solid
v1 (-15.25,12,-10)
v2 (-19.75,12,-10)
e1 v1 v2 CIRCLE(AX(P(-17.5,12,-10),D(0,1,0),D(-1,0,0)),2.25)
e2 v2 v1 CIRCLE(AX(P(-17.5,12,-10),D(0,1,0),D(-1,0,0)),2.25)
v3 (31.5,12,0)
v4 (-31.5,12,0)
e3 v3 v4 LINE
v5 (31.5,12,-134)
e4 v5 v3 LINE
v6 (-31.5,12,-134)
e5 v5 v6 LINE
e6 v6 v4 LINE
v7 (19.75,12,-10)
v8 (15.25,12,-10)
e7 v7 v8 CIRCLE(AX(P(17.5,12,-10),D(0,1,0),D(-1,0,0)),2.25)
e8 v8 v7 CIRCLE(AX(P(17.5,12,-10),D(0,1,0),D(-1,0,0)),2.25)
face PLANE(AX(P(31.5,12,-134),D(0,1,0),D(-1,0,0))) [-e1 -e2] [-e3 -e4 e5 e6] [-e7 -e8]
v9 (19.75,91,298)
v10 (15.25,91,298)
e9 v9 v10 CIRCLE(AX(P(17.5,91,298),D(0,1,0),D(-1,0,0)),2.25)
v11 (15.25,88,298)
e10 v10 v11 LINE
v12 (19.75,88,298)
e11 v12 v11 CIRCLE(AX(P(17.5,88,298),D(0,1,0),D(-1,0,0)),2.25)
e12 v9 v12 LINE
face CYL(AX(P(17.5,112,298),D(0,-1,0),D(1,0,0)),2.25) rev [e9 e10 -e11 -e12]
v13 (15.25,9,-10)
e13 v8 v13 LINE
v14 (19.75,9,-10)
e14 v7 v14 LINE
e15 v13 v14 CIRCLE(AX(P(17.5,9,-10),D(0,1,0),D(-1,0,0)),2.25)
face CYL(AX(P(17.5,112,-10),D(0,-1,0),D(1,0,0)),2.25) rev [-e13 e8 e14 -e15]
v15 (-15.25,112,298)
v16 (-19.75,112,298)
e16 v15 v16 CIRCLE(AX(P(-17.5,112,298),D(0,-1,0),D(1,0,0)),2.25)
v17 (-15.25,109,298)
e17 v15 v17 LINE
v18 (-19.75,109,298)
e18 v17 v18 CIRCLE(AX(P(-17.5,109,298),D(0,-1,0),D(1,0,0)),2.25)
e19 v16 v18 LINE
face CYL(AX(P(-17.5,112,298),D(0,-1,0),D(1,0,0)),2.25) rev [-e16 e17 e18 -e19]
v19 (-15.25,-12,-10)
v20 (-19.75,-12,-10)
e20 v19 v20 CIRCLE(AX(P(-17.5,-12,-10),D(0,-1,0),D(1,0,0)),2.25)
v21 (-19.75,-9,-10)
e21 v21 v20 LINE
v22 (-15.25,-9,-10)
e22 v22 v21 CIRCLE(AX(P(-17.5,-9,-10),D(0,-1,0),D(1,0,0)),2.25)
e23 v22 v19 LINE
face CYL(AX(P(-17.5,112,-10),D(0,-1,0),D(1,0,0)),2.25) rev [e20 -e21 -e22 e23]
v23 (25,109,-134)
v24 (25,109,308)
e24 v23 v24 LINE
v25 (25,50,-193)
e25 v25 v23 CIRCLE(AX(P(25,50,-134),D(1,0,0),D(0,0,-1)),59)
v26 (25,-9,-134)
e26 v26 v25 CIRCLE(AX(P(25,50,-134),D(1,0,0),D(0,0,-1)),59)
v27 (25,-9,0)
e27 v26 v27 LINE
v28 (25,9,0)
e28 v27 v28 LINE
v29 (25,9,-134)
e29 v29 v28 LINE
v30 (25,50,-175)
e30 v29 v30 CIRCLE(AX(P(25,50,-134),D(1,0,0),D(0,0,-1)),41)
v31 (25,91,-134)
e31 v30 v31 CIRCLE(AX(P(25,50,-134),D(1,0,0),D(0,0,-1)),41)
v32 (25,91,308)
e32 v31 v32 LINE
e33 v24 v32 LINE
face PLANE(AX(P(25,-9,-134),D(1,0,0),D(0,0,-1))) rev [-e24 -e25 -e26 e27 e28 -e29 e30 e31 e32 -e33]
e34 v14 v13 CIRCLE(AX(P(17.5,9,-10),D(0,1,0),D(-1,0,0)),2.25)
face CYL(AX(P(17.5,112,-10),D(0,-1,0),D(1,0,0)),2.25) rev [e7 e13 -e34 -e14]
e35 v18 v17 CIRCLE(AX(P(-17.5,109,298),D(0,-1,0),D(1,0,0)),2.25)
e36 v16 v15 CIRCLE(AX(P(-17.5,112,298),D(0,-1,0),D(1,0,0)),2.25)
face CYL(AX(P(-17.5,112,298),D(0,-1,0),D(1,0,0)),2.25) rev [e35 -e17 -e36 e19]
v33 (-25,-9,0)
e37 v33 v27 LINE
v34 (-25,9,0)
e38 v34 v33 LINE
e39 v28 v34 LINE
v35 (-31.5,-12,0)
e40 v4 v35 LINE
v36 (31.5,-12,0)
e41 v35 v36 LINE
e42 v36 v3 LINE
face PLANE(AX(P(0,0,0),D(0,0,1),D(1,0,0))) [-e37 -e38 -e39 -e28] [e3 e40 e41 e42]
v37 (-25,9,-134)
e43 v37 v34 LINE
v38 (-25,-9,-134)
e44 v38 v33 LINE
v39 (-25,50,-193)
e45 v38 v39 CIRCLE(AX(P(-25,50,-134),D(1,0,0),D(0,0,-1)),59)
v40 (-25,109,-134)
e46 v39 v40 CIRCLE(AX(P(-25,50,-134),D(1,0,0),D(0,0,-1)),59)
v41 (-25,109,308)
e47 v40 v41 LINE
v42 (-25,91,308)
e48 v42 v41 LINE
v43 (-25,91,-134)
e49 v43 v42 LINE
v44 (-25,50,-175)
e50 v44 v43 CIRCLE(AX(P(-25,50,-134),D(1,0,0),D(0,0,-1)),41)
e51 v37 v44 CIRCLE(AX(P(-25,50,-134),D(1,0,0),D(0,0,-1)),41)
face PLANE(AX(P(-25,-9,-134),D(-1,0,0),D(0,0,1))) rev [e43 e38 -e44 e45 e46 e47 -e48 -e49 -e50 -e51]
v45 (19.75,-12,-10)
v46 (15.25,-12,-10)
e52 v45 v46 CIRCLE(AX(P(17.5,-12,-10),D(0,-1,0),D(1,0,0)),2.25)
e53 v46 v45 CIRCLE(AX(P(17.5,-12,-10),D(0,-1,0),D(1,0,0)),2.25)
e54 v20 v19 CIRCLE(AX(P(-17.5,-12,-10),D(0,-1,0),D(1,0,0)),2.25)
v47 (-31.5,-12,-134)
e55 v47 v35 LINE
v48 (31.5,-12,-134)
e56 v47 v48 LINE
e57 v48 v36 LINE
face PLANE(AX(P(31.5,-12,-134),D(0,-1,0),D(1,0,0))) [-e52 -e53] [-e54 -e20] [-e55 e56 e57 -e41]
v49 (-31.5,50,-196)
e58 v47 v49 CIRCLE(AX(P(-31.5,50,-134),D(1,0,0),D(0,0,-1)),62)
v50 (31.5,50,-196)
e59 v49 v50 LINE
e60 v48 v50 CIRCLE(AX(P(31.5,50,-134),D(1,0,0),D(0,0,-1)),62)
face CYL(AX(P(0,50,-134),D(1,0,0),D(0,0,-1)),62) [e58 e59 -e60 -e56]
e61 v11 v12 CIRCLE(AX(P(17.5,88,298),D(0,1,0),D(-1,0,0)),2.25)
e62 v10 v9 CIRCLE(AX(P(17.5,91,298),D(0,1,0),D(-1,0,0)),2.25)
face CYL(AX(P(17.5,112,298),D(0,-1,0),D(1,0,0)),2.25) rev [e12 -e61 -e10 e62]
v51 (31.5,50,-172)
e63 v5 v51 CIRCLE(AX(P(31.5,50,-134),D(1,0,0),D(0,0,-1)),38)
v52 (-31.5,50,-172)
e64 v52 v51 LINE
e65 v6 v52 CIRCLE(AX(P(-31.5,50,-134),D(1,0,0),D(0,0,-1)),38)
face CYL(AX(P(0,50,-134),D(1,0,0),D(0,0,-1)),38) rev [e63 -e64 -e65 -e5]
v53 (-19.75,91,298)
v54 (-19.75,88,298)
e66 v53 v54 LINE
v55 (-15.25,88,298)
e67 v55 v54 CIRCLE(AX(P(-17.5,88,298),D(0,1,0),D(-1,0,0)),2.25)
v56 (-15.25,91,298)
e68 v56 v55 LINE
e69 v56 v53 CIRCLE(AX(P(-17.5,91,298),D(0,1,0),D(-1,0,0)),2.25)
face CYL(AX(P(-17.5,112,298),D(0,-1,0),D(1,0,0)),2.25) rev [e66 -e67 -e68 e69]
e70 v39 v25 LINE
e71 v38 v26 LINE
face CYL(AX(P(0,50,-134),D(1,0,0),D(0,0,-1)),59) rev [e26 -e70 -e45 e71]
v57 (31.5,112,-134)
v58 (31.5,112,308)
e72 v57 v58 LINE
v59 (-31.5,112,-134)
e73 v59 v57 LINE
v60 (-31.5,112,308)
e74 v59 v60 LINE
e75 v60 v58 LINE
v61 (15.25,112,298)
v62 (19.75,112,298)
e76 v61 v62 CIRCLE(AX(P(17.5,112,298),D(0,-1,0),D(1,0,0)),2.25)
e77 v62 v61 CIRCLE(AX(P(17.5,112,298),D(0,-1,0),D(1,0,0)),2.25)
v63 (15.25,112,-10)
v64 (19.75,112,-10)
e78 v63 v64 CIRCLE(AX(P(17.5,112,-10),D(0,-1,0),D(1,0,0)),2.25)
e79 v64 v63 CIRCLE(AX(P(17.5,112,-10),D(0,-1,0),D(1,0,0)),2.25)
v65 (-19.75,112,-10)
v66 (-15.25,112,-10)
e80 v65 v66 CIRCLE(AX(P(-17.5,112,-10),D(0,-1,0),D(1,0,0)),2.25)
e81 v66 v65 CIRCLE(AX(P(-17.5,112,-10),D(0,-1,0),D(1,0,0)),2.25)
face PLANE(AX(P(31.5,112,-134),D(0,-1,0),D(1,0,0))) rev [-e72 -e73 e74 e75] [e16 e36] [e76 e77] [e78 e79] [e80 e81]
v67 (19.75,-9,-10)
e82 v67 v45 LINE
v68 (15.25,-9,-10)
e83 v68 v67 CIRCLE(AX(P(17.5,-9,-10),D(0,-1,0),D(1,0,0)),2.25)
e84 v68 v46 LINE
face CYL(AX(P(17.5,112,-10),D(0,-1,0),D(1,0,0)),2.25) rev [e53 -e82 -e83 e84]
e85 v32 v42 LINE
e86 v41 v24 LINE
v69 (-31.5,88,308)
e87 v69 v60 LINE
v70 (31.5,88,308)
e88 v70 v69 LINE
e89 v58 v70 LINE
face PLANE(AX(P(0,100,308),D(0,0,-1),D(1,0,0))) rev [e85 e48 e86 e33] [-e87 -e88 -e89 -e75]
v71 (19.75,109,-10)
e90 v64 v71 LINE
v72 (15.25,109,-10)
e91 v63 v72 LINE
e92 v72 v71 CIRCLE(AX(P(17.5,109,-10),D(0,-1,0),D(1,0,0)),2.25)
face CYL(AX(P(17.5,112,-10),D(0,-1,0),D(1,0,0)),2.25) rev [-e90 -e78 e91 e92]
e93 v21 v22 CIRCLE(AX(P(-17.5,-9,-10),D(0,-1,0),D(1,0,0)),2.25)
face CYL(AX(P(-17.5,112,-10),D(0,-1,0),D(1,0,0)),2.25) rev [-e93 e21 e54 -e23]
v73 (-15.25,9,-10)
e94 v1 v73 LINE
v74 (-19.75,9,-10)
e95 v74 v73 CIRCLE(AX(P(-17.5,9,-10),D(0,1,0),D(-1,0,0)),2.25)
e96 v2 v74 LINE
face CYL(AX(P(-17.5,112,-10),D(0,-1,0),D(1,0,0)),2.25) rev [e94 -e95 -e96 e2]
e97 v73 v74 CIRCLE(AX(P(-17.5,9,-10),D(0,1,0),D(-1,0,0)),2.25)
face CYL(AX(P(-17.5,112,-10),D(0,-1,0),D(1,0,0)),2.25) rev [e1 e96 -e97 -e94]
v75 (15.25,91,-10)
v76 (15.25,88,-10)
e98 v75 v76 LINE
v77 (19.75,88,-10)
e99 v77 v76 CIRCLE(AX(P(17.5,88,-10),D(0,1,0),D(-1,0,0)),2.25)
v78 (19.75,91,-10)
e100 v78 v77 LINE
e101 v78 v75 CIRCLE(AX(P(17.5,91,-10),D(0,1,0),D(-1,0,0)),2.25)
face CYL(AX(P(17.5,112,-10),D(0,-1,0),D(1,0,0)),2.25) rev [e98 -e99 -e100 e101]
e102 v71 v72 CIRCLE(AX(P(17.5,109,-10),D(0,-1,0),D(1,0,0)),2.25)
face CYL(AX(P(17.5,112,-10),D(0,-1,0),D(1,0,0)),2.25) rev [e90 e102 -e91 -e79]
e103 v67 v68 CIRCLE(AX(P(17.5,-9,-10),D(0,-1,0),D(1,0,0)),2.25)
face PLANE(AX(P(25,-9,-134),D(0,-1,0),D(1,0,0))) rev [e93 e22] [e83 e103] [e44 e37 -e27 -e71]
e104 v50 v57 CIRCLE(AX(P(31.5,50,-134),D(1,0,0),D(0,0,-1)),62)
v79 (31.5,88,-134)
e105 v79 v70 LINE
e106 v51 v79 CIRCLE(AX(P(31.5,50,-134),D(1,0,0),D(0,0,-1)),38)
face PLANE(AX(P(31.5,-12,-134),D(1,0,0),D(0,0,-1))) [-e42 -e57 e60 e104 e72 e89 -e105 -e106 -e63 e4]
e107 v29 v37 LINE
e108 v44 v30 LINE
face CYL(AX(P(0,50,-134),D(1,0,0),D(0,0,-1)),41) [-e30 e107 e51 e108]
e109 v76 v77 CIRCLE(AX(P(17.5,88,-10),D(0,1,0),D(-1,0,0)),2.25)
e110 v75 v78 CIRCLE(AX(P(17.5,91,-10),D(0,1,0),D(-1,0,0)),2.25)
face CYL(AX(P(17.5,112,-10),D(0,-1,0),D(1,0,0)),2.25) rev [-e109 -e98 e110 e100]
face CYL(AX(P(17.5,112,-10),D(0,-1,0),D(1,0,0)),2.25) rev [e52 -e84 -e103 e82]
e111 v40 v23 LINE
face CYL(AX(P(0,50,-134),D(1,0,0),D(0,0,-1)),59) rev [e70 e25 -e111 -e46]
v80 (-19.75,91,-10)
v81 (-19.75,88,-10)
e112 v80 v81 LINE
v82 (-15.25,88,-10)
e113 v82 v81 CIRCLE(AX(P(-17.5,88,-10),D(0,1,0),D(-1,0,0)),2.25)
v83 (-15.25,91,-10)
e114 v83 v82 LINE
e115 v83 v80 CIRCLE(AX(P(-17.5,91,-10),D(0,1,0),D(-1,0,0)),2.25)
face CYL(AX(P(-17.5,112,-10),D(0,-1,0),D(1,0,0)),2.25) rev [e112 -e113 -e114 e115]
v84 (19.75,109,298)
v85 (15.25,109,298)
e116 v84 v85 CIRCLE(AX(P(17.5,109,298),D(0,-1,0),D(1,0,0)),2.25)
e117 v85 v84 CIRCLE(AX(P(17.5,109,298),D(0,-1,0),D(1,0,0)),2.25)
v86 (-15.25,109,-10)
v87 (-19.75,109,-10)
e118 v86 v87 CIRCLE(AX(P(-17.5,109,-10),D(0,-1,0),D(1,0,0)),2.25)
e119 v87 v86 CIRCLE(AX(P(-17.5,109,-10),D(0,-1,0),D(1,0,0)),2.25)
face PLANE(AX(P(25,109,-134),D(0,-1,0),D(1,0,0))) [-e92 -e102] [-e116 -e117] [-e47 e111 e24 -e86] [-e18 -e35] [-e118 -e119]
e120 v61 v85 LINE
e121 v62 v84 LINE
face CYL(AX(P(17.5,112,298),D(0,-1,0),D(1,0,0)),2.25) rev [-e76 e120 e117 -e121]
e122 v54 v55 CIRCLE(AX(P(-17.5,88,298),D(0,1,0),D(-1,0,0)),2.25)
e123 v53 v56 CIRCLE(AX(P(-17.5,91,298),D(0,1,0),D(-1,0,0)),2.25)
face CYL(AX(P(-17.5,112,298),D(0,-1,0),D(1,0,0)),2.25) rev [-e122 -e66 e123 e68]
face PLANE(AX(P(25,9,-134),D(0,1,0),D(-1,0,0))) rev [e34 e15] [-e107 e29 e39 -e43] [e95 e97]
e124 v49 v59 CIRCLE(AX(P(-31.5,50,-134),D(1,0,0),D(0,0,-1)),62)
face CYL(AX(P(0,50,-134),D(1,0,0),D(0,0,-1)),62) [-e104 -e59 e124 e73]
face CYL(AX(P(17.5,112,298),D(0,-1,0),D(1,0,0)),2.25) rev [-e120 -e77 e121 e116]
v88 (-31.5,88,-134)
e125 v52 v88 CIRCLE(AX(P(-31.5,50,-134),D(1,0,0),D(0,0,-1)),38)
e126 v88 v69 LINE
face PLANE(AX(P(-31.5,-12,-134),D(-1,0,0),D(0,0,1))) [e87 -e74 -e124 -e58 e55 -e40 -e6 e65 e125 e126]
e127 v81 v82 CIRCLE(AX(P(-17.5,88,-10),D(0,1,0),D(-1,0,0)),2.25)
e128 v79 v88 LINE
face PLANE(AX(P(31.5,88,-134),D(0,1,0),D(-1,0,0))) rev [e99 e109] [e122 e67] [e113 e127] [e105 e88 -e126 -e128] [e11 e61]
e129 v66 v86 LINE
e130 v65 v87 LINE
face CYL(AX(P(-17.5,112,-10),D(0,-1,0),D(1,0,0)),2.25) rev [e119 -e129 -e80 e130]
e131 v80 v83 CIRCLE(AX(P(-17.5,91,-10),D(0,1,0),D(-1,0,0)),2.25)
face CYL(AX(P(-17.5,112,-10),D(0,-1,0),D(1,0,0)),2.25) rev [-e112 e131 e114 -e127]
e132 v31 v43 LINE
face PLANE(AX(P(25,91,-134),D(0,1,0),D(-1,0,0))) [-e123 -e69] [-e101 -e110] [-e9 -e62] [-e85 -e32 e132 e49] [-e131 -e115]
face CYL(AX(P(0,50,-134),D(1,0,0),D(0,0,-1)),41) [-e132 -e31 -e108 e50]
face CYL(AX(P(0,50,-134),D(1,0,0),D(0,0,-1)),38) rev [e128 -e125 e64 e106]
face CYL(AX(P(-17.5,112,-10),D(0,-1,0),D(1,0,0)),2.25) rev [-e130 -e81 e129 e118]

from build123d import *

# Parameters (mm, degrees)
SKETCH_1_W          = 63
SKETCH_1_H          = 24
SKETCH_1_W_2        = 50
SKETCH_1_H_2        = 18
SKETCH_5_R          = 2.25
CUT_EXTRUDE_3_DEPTH = 334.514992167


with BuildPart() as part:
    # 扫描1: sweep along a path in 草图2
    with BuildLine(Plane(origin=(0, 0, 0), x_dir=(0, 0, -1), z_dir=(1, 0, 0))) as sweep_1_path:
        Line((0, 0), (134, 0))
        ThreePointArc((134, 0), (184, 50), (134, 100))
        Line((134, 100), (-308, 100))
    # 草图1 → 扫描1 (sweep)
    with BuildSketch(Plane.XY):
        Rectangle(SKETCH_1_W, SKETCH_1_H)
        Rectangle(SKETCH_1_W_2, SKETCH_1_H_2, mode=Mode.SUBTRACT)
    sweep(path=sweep_1_path.line)

    # 草图5 → 切除-拉伸3 (cut, through all)
    with BuildSketch(Plane.XZ.offset(12)):
        with Locations((-17.5, -10)):
            Circle(SKETCH_5_R)
        with Locations((17.5, -10)):
            Circle(SKETCH_5_R)
        with Locations(Location((-17.5, 298, 0), (0, 0, 180))):
            Circle(SKETCH_5_R)
        with Locations(Location((17.5, 298, 0), (0, 0, 180))):
            Circle(SKETCH_5_R)
    extrude(amount=-CUT_EXTRUDE_3_DEPTH, mode=Mode.SUBTRACT)


solid = part.part
